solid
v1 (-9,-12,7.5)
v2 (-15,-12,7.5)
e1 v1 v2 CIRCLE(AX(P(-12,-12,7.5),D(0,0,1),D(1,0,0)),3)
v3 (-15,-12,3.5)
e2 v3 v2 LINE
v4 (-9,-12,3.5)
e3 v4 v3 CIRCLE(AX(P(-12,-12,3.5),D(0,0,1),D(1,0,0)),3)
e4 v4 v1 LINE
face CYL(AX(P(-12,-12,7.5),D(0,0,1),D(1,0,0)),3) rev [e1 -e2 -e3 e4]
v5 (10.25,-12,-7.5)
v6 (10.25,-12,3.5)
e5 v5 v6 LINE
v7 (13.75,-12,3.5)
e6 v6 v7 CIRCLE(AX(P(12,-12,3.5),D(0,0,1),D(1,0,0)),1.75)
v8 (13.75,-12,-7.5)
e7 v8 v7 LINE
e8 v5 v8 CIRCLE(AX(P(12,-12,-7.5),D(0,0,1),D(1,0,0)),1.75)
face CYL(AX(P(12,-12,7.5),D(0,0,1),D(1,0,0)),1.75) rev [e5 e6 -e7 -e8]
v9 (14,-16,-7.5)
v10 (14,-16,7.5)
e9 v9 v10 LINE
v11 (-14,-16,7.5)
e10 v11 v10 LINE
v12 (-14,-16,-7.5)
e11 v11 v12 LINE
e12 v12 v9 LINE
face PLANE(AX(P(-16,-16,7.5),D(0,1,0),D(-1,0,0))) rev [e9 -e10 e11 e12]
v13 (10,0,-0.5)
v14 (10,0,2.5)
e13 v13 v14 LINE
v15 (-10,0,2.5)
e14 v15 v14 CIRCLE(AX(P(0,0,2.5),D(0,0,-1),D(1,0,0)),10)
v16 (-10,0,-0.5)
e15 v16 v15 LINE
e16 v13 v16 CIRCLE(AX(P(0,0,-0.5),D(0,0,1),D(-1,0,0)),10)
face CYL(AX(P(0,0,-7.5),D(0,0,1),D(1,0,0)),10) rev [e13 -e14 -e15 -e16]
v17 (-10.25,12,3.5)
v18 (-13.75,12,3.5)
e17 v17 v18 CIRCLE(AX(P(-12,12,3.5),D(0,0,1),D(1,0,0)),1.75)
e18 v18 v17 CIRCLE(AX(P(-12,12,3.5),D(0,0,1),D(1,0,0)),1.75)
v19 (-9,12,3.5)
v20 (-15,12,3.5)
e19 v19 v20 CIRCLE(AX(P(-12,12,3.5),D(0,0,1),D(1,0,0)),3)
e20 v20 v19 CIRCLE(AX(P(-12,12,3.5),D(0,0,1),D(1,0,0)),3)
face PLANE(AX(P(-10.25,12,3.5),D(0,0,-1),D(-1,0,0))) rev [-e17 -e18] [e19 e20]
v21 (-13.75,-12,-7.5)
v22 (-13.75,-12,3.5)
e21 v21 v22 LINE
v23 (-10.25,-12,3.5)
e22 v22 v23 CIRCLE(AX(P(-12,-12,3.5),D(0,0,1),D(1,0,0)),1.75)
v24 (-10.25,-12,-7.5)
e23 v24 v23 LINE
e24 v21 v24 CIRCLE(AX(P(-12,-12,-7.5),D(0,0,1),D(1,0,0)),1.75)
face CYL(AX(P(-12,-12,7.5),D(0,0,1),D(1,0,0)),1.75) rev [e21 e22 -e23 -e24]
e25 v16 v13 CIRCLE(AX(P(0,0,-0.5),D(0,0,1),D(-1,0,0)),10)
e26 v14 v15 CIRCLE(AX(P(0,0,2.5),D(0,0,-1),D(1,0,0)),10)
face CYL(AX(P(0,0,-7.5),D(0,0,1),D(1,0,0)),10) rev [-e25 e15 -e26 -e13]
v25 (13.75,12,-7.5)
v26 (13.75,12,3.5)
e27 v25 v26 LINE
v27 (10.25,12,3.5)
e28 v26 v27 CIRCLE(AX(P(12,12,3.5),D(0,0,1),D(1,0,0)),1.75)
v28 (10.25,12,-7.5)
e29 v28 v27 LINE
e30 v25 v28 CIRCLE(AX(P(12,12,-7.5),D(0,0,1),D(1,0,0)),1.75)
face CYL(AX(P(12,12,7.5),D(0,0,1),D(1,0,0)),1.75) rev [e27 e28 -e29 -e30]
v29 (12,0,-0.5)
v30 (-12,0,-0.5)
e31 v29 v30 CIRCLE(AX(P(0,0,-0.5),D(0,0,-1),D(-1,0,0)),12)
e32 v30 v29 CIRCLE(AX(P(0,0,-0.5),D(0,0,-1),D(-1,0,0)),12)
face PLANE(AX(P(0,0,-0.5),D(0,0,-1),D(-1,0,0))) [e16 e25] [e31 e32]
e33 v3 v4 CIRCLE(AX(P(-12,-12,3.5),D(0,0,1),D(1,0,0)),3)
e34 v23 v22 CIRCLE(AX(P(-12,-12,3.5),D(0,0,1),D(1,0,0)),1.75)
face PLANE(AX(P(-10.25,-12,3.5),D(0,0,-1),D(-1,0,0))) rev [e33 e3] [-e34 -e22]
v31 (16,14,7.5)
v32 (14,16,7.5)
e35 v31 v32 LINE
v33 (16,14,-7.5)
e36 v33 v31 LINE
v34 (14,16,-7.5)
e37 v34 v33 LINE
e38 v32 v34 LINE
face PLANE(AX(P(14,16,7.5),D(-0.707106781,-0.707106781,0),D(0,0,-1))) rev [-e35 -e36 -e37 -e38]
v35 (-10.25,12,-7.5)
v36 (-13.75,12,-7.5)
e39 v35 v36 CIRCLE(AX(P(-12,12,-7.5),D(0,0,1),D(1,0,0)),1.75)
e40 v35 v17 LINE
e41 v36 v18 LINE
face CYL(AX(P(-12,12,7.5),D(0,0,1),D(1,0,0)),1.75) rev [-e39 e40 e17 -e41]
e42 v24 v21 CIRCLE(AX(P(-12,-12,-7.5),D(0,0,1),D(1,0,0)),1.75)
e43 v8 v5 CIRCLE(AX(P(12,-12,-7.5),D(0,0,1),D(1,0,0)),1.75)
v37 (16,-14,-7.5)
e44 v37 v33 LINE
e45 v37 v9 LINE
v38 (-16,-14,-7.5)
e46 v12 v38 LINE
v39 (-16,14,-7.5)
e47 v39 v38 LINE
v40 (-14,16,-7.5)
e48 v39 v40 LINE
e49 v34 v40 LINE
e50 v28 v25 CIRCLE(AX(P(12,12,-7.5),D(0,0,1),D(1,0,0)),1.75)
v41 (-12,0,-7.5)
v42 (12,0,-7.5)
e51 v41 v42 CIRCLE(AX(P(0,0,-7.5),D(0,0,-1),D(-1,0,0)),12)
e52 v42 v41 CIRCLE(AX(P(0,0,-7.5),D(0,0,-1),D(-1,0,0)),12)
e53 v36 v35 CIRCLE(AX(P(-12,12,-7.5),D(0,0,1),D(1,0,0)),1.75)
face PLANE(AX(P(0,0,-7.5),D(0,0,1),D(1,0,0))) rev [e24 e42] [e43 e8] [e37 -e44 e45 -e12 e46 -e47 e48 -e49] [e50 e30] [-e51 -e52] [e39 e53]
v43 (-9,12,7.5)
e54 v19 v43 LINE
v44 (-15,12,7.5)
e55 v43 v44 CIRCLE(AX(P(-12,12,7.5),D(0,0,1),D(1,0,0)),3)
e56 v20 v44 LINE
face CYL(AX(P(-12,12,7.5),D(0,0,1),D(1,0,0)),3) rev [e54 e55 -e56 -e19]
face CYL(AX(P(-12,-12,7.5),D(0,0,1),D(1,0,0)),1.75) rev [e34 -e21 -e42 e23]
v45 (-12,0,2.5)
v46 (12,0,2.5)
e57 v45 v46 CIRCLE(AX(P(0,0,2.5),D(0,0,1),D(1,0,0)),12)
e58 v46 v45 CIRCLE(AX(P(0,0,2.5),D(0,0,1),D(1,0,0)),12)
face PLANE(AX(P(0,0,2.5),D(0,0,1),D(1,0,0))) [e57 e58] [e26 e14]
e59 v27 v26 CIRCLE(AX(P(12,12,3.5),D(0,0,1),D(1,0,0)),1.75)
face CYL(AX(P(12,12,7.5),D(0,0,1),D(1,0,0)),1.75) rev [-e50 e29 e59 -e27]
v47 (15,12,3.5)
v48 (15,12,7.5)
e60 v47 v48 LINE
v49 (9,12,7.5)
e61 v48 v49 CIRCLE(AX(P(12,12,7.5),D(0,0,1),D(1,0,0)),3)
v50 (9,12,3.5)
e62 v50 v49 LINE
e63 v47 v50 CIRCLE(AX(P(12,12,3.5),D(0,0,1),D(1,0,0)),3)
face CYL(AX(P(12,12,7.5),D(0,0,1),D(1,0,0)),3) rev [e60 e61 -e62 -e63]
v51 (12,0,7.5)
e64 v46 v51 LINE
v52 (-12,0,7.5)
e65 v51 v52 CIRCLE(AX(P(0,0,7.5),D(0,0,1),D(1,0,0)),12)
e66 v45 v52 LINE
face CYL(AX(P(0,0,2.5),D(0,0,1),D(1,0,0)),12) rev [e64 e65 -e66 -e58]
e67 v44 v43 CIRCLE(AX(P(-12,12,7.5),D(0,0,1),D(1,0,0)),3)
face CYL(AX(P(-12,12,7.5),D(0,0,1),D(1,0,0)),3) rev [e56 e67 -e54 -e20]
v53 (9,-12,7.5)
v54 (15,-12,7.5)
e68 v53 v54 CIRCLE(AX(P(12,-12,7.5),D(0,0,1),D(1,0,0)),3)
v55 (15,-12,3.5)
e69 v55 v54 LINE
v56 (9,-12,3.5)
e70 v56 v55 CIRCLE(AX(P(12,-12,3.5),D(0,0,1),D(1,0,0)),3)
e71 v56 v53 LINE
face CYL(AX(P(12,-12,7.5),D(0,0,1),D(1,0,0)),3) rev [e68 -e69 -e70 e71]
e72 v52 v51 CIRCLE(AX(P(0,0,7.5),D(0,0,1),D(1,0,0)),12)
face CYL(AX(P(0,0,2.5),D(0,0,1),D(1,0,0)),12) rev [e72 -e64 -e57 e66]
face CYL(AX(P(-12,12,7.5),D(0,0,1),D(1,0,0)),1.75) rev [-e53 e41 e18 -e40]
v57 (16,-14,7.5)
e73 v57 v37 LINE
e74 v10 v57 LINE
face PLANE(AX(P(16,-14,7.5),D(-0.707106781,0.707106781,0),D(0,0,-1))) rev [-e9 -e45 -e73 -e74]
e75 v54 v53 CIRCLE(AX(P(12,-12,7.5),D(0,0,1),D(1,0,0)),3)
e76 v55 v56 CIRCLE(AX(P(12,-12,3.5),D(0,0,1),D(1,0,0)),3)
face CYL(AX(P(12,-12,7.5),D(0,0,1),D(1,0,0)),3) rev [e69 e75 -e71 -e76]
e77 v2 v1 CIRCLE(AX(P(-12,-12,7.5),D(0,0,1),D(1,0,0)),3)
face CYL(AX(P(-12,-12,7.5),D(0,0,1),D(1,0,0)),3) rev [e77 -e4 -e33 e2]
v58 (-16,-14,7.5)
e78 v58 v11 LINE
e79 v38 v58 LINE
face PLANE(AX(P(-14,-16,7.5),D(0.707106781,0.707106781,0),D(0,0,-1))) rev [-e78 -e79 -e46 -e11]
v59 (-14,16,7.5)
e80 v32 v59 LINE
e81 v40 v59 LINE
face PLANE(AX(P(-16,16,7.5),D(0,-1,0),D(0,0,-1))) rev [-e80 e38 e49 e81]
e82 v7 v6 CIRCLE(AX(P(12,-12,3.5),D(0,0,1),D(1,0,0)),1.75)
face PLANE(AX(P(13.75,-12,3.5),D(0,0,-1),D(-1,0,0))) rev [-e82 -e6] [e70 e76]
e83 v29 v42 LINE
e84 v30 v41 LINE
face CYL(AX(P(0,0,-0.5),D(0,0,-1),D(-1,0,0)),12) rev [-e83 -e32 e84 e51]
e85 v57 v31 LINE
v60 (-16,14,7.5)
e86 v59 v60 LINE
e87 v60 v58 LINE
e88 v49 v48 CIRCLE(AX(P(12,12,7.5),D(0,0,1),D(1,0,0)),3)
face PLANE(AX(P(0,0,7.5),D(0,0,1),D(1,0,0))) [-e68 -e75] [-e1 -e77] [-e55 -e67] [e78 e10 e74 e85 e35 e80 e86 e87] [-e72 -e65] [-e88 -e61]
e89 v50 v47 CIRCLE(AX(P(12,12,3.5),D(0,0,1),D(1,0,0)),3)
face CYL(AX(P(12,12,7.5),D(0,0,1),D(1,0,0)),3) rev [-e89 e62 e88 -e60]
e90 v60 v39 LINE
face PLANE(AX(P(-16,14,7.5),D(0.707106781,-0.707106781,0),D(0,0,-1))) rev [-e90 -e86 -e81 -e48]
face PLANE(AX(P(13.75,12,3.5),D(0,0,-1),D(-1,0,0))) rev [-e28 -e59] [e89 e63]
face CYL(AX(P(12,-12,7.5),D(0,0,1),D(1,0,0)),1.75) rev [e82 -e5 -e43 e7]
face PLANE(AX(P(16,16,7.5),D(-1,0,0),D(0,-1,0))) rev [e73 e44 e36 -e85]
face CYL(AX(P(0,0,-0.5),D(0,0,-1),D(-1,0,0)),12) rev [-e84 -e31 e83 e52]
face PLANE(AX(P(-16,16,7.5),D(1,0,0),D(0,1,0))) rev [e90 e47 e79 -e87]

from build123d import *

# Parameters (mm, degrees)
SKETCH1_W                                            = 32
SKETCH1_H                                            = 32
BOSS_EXTRUDE1_DEPTH                                  = 7.5
SKETCH2_R                                            = 10
CUT_EXTRUDE1_DEPTH                                   = 28.147743921
SKETCH3_R                                            = 12
CUT_EXTRUDE2_DEPTH                                   = 5
CUT_EXTRUDE3_START                                   = -7
SKETCH4_R                                            = 12
CUT_EXTRUDE3_DEPTH                                   = 7
CHAMFER1_SIZE                                        = 2
HOLE_SIZE_PER_SOCKET_HEAD_CAP_SCREW_TYPE_D           = 3.5
HOLE_SIZE_PER_SOCKET_HEAD_CAP_SCREW_TYPE_CBORE_D     = 6
HOLE_SIZE_PER_SOCKET_HEAD_CAP_SCREW_TYPE_CBORE_DEPTH = 4


with BuildPart() as part:
    # Sketch1 → Boss-Extrude1 (new, symmetric)
    with BuildSketch(Plane.XY):
        Rectangle(SKETCH1_W, SKETCH1_H)
    extrude(amount=BOSS_EXTRUDE1_DEPTH, both=True)

    # Sketch2 → Cut-Extrude1 (cut, through all)
    with BuildSketch(Plane.XY.offset(7.5)):
        Circle(SKETCH2_R)
    extrude(amount=-CUT_EXTRUDE1_DEPTH, mode=Mode.SUBTRACT)

    # Sketch3 → Cut-Extrude2 (cut)
    with BuildSketch(Plane.XY.offset(7.5)):
        Circle(SKETCH3_R)
    extrude(amount=-CUT_EXTRUDE2_DEPTH, mode=Mode.SUBTRACT)

    # Sketch4 → Cut-Extrude3 (cut)
    with BuildSketch(Plane(origin=(0, 0, -7.5), x_dir=(-1, 0, 0), z_dir=(0, 0, -1)).offset(CUT_EXTRUDE3_START)):
        with Locations(Location((0, 0, 0), (0, 0, 180))):
            Circle(SKETCH4_R)
    extrude(amount=CUT_EXTRUDE3_DEPTH, mode=Mode.SUBTRACT)

    # Chamfer1
    chamfer1_edges = [part.edges().sort_by_distance(p)[0] for p in [
        (16, -16, 0),
        (-16, -16, 0),
        (-16, 16, 0),
        (16, 16, 0),
    ]]
    chamfer(chamfer1_edges, length=CHAMFER1_SIZE)

    # Hole size per socket head cap screw type1 (through all)
    with Locations(Plane.XY.offset(7.5)):
        with Locations((-12, 12), (12, 12), (12, -12), (-12, -12)):
            CounterBoreHole(HOLE_SIZE_PER_SOCKET_HEAD_CAP_SCREW_TYPE_D / 2, HOLE_SIZE_PER_SOCKET_HEAD_CAP_SCREW_TYPE_CBORE_D / 2, HOLE_SIZE_PER_SOCKET_HEAD_CAP_SCREW_TYPE_CBORE_DEPTH)


solid = part.part
